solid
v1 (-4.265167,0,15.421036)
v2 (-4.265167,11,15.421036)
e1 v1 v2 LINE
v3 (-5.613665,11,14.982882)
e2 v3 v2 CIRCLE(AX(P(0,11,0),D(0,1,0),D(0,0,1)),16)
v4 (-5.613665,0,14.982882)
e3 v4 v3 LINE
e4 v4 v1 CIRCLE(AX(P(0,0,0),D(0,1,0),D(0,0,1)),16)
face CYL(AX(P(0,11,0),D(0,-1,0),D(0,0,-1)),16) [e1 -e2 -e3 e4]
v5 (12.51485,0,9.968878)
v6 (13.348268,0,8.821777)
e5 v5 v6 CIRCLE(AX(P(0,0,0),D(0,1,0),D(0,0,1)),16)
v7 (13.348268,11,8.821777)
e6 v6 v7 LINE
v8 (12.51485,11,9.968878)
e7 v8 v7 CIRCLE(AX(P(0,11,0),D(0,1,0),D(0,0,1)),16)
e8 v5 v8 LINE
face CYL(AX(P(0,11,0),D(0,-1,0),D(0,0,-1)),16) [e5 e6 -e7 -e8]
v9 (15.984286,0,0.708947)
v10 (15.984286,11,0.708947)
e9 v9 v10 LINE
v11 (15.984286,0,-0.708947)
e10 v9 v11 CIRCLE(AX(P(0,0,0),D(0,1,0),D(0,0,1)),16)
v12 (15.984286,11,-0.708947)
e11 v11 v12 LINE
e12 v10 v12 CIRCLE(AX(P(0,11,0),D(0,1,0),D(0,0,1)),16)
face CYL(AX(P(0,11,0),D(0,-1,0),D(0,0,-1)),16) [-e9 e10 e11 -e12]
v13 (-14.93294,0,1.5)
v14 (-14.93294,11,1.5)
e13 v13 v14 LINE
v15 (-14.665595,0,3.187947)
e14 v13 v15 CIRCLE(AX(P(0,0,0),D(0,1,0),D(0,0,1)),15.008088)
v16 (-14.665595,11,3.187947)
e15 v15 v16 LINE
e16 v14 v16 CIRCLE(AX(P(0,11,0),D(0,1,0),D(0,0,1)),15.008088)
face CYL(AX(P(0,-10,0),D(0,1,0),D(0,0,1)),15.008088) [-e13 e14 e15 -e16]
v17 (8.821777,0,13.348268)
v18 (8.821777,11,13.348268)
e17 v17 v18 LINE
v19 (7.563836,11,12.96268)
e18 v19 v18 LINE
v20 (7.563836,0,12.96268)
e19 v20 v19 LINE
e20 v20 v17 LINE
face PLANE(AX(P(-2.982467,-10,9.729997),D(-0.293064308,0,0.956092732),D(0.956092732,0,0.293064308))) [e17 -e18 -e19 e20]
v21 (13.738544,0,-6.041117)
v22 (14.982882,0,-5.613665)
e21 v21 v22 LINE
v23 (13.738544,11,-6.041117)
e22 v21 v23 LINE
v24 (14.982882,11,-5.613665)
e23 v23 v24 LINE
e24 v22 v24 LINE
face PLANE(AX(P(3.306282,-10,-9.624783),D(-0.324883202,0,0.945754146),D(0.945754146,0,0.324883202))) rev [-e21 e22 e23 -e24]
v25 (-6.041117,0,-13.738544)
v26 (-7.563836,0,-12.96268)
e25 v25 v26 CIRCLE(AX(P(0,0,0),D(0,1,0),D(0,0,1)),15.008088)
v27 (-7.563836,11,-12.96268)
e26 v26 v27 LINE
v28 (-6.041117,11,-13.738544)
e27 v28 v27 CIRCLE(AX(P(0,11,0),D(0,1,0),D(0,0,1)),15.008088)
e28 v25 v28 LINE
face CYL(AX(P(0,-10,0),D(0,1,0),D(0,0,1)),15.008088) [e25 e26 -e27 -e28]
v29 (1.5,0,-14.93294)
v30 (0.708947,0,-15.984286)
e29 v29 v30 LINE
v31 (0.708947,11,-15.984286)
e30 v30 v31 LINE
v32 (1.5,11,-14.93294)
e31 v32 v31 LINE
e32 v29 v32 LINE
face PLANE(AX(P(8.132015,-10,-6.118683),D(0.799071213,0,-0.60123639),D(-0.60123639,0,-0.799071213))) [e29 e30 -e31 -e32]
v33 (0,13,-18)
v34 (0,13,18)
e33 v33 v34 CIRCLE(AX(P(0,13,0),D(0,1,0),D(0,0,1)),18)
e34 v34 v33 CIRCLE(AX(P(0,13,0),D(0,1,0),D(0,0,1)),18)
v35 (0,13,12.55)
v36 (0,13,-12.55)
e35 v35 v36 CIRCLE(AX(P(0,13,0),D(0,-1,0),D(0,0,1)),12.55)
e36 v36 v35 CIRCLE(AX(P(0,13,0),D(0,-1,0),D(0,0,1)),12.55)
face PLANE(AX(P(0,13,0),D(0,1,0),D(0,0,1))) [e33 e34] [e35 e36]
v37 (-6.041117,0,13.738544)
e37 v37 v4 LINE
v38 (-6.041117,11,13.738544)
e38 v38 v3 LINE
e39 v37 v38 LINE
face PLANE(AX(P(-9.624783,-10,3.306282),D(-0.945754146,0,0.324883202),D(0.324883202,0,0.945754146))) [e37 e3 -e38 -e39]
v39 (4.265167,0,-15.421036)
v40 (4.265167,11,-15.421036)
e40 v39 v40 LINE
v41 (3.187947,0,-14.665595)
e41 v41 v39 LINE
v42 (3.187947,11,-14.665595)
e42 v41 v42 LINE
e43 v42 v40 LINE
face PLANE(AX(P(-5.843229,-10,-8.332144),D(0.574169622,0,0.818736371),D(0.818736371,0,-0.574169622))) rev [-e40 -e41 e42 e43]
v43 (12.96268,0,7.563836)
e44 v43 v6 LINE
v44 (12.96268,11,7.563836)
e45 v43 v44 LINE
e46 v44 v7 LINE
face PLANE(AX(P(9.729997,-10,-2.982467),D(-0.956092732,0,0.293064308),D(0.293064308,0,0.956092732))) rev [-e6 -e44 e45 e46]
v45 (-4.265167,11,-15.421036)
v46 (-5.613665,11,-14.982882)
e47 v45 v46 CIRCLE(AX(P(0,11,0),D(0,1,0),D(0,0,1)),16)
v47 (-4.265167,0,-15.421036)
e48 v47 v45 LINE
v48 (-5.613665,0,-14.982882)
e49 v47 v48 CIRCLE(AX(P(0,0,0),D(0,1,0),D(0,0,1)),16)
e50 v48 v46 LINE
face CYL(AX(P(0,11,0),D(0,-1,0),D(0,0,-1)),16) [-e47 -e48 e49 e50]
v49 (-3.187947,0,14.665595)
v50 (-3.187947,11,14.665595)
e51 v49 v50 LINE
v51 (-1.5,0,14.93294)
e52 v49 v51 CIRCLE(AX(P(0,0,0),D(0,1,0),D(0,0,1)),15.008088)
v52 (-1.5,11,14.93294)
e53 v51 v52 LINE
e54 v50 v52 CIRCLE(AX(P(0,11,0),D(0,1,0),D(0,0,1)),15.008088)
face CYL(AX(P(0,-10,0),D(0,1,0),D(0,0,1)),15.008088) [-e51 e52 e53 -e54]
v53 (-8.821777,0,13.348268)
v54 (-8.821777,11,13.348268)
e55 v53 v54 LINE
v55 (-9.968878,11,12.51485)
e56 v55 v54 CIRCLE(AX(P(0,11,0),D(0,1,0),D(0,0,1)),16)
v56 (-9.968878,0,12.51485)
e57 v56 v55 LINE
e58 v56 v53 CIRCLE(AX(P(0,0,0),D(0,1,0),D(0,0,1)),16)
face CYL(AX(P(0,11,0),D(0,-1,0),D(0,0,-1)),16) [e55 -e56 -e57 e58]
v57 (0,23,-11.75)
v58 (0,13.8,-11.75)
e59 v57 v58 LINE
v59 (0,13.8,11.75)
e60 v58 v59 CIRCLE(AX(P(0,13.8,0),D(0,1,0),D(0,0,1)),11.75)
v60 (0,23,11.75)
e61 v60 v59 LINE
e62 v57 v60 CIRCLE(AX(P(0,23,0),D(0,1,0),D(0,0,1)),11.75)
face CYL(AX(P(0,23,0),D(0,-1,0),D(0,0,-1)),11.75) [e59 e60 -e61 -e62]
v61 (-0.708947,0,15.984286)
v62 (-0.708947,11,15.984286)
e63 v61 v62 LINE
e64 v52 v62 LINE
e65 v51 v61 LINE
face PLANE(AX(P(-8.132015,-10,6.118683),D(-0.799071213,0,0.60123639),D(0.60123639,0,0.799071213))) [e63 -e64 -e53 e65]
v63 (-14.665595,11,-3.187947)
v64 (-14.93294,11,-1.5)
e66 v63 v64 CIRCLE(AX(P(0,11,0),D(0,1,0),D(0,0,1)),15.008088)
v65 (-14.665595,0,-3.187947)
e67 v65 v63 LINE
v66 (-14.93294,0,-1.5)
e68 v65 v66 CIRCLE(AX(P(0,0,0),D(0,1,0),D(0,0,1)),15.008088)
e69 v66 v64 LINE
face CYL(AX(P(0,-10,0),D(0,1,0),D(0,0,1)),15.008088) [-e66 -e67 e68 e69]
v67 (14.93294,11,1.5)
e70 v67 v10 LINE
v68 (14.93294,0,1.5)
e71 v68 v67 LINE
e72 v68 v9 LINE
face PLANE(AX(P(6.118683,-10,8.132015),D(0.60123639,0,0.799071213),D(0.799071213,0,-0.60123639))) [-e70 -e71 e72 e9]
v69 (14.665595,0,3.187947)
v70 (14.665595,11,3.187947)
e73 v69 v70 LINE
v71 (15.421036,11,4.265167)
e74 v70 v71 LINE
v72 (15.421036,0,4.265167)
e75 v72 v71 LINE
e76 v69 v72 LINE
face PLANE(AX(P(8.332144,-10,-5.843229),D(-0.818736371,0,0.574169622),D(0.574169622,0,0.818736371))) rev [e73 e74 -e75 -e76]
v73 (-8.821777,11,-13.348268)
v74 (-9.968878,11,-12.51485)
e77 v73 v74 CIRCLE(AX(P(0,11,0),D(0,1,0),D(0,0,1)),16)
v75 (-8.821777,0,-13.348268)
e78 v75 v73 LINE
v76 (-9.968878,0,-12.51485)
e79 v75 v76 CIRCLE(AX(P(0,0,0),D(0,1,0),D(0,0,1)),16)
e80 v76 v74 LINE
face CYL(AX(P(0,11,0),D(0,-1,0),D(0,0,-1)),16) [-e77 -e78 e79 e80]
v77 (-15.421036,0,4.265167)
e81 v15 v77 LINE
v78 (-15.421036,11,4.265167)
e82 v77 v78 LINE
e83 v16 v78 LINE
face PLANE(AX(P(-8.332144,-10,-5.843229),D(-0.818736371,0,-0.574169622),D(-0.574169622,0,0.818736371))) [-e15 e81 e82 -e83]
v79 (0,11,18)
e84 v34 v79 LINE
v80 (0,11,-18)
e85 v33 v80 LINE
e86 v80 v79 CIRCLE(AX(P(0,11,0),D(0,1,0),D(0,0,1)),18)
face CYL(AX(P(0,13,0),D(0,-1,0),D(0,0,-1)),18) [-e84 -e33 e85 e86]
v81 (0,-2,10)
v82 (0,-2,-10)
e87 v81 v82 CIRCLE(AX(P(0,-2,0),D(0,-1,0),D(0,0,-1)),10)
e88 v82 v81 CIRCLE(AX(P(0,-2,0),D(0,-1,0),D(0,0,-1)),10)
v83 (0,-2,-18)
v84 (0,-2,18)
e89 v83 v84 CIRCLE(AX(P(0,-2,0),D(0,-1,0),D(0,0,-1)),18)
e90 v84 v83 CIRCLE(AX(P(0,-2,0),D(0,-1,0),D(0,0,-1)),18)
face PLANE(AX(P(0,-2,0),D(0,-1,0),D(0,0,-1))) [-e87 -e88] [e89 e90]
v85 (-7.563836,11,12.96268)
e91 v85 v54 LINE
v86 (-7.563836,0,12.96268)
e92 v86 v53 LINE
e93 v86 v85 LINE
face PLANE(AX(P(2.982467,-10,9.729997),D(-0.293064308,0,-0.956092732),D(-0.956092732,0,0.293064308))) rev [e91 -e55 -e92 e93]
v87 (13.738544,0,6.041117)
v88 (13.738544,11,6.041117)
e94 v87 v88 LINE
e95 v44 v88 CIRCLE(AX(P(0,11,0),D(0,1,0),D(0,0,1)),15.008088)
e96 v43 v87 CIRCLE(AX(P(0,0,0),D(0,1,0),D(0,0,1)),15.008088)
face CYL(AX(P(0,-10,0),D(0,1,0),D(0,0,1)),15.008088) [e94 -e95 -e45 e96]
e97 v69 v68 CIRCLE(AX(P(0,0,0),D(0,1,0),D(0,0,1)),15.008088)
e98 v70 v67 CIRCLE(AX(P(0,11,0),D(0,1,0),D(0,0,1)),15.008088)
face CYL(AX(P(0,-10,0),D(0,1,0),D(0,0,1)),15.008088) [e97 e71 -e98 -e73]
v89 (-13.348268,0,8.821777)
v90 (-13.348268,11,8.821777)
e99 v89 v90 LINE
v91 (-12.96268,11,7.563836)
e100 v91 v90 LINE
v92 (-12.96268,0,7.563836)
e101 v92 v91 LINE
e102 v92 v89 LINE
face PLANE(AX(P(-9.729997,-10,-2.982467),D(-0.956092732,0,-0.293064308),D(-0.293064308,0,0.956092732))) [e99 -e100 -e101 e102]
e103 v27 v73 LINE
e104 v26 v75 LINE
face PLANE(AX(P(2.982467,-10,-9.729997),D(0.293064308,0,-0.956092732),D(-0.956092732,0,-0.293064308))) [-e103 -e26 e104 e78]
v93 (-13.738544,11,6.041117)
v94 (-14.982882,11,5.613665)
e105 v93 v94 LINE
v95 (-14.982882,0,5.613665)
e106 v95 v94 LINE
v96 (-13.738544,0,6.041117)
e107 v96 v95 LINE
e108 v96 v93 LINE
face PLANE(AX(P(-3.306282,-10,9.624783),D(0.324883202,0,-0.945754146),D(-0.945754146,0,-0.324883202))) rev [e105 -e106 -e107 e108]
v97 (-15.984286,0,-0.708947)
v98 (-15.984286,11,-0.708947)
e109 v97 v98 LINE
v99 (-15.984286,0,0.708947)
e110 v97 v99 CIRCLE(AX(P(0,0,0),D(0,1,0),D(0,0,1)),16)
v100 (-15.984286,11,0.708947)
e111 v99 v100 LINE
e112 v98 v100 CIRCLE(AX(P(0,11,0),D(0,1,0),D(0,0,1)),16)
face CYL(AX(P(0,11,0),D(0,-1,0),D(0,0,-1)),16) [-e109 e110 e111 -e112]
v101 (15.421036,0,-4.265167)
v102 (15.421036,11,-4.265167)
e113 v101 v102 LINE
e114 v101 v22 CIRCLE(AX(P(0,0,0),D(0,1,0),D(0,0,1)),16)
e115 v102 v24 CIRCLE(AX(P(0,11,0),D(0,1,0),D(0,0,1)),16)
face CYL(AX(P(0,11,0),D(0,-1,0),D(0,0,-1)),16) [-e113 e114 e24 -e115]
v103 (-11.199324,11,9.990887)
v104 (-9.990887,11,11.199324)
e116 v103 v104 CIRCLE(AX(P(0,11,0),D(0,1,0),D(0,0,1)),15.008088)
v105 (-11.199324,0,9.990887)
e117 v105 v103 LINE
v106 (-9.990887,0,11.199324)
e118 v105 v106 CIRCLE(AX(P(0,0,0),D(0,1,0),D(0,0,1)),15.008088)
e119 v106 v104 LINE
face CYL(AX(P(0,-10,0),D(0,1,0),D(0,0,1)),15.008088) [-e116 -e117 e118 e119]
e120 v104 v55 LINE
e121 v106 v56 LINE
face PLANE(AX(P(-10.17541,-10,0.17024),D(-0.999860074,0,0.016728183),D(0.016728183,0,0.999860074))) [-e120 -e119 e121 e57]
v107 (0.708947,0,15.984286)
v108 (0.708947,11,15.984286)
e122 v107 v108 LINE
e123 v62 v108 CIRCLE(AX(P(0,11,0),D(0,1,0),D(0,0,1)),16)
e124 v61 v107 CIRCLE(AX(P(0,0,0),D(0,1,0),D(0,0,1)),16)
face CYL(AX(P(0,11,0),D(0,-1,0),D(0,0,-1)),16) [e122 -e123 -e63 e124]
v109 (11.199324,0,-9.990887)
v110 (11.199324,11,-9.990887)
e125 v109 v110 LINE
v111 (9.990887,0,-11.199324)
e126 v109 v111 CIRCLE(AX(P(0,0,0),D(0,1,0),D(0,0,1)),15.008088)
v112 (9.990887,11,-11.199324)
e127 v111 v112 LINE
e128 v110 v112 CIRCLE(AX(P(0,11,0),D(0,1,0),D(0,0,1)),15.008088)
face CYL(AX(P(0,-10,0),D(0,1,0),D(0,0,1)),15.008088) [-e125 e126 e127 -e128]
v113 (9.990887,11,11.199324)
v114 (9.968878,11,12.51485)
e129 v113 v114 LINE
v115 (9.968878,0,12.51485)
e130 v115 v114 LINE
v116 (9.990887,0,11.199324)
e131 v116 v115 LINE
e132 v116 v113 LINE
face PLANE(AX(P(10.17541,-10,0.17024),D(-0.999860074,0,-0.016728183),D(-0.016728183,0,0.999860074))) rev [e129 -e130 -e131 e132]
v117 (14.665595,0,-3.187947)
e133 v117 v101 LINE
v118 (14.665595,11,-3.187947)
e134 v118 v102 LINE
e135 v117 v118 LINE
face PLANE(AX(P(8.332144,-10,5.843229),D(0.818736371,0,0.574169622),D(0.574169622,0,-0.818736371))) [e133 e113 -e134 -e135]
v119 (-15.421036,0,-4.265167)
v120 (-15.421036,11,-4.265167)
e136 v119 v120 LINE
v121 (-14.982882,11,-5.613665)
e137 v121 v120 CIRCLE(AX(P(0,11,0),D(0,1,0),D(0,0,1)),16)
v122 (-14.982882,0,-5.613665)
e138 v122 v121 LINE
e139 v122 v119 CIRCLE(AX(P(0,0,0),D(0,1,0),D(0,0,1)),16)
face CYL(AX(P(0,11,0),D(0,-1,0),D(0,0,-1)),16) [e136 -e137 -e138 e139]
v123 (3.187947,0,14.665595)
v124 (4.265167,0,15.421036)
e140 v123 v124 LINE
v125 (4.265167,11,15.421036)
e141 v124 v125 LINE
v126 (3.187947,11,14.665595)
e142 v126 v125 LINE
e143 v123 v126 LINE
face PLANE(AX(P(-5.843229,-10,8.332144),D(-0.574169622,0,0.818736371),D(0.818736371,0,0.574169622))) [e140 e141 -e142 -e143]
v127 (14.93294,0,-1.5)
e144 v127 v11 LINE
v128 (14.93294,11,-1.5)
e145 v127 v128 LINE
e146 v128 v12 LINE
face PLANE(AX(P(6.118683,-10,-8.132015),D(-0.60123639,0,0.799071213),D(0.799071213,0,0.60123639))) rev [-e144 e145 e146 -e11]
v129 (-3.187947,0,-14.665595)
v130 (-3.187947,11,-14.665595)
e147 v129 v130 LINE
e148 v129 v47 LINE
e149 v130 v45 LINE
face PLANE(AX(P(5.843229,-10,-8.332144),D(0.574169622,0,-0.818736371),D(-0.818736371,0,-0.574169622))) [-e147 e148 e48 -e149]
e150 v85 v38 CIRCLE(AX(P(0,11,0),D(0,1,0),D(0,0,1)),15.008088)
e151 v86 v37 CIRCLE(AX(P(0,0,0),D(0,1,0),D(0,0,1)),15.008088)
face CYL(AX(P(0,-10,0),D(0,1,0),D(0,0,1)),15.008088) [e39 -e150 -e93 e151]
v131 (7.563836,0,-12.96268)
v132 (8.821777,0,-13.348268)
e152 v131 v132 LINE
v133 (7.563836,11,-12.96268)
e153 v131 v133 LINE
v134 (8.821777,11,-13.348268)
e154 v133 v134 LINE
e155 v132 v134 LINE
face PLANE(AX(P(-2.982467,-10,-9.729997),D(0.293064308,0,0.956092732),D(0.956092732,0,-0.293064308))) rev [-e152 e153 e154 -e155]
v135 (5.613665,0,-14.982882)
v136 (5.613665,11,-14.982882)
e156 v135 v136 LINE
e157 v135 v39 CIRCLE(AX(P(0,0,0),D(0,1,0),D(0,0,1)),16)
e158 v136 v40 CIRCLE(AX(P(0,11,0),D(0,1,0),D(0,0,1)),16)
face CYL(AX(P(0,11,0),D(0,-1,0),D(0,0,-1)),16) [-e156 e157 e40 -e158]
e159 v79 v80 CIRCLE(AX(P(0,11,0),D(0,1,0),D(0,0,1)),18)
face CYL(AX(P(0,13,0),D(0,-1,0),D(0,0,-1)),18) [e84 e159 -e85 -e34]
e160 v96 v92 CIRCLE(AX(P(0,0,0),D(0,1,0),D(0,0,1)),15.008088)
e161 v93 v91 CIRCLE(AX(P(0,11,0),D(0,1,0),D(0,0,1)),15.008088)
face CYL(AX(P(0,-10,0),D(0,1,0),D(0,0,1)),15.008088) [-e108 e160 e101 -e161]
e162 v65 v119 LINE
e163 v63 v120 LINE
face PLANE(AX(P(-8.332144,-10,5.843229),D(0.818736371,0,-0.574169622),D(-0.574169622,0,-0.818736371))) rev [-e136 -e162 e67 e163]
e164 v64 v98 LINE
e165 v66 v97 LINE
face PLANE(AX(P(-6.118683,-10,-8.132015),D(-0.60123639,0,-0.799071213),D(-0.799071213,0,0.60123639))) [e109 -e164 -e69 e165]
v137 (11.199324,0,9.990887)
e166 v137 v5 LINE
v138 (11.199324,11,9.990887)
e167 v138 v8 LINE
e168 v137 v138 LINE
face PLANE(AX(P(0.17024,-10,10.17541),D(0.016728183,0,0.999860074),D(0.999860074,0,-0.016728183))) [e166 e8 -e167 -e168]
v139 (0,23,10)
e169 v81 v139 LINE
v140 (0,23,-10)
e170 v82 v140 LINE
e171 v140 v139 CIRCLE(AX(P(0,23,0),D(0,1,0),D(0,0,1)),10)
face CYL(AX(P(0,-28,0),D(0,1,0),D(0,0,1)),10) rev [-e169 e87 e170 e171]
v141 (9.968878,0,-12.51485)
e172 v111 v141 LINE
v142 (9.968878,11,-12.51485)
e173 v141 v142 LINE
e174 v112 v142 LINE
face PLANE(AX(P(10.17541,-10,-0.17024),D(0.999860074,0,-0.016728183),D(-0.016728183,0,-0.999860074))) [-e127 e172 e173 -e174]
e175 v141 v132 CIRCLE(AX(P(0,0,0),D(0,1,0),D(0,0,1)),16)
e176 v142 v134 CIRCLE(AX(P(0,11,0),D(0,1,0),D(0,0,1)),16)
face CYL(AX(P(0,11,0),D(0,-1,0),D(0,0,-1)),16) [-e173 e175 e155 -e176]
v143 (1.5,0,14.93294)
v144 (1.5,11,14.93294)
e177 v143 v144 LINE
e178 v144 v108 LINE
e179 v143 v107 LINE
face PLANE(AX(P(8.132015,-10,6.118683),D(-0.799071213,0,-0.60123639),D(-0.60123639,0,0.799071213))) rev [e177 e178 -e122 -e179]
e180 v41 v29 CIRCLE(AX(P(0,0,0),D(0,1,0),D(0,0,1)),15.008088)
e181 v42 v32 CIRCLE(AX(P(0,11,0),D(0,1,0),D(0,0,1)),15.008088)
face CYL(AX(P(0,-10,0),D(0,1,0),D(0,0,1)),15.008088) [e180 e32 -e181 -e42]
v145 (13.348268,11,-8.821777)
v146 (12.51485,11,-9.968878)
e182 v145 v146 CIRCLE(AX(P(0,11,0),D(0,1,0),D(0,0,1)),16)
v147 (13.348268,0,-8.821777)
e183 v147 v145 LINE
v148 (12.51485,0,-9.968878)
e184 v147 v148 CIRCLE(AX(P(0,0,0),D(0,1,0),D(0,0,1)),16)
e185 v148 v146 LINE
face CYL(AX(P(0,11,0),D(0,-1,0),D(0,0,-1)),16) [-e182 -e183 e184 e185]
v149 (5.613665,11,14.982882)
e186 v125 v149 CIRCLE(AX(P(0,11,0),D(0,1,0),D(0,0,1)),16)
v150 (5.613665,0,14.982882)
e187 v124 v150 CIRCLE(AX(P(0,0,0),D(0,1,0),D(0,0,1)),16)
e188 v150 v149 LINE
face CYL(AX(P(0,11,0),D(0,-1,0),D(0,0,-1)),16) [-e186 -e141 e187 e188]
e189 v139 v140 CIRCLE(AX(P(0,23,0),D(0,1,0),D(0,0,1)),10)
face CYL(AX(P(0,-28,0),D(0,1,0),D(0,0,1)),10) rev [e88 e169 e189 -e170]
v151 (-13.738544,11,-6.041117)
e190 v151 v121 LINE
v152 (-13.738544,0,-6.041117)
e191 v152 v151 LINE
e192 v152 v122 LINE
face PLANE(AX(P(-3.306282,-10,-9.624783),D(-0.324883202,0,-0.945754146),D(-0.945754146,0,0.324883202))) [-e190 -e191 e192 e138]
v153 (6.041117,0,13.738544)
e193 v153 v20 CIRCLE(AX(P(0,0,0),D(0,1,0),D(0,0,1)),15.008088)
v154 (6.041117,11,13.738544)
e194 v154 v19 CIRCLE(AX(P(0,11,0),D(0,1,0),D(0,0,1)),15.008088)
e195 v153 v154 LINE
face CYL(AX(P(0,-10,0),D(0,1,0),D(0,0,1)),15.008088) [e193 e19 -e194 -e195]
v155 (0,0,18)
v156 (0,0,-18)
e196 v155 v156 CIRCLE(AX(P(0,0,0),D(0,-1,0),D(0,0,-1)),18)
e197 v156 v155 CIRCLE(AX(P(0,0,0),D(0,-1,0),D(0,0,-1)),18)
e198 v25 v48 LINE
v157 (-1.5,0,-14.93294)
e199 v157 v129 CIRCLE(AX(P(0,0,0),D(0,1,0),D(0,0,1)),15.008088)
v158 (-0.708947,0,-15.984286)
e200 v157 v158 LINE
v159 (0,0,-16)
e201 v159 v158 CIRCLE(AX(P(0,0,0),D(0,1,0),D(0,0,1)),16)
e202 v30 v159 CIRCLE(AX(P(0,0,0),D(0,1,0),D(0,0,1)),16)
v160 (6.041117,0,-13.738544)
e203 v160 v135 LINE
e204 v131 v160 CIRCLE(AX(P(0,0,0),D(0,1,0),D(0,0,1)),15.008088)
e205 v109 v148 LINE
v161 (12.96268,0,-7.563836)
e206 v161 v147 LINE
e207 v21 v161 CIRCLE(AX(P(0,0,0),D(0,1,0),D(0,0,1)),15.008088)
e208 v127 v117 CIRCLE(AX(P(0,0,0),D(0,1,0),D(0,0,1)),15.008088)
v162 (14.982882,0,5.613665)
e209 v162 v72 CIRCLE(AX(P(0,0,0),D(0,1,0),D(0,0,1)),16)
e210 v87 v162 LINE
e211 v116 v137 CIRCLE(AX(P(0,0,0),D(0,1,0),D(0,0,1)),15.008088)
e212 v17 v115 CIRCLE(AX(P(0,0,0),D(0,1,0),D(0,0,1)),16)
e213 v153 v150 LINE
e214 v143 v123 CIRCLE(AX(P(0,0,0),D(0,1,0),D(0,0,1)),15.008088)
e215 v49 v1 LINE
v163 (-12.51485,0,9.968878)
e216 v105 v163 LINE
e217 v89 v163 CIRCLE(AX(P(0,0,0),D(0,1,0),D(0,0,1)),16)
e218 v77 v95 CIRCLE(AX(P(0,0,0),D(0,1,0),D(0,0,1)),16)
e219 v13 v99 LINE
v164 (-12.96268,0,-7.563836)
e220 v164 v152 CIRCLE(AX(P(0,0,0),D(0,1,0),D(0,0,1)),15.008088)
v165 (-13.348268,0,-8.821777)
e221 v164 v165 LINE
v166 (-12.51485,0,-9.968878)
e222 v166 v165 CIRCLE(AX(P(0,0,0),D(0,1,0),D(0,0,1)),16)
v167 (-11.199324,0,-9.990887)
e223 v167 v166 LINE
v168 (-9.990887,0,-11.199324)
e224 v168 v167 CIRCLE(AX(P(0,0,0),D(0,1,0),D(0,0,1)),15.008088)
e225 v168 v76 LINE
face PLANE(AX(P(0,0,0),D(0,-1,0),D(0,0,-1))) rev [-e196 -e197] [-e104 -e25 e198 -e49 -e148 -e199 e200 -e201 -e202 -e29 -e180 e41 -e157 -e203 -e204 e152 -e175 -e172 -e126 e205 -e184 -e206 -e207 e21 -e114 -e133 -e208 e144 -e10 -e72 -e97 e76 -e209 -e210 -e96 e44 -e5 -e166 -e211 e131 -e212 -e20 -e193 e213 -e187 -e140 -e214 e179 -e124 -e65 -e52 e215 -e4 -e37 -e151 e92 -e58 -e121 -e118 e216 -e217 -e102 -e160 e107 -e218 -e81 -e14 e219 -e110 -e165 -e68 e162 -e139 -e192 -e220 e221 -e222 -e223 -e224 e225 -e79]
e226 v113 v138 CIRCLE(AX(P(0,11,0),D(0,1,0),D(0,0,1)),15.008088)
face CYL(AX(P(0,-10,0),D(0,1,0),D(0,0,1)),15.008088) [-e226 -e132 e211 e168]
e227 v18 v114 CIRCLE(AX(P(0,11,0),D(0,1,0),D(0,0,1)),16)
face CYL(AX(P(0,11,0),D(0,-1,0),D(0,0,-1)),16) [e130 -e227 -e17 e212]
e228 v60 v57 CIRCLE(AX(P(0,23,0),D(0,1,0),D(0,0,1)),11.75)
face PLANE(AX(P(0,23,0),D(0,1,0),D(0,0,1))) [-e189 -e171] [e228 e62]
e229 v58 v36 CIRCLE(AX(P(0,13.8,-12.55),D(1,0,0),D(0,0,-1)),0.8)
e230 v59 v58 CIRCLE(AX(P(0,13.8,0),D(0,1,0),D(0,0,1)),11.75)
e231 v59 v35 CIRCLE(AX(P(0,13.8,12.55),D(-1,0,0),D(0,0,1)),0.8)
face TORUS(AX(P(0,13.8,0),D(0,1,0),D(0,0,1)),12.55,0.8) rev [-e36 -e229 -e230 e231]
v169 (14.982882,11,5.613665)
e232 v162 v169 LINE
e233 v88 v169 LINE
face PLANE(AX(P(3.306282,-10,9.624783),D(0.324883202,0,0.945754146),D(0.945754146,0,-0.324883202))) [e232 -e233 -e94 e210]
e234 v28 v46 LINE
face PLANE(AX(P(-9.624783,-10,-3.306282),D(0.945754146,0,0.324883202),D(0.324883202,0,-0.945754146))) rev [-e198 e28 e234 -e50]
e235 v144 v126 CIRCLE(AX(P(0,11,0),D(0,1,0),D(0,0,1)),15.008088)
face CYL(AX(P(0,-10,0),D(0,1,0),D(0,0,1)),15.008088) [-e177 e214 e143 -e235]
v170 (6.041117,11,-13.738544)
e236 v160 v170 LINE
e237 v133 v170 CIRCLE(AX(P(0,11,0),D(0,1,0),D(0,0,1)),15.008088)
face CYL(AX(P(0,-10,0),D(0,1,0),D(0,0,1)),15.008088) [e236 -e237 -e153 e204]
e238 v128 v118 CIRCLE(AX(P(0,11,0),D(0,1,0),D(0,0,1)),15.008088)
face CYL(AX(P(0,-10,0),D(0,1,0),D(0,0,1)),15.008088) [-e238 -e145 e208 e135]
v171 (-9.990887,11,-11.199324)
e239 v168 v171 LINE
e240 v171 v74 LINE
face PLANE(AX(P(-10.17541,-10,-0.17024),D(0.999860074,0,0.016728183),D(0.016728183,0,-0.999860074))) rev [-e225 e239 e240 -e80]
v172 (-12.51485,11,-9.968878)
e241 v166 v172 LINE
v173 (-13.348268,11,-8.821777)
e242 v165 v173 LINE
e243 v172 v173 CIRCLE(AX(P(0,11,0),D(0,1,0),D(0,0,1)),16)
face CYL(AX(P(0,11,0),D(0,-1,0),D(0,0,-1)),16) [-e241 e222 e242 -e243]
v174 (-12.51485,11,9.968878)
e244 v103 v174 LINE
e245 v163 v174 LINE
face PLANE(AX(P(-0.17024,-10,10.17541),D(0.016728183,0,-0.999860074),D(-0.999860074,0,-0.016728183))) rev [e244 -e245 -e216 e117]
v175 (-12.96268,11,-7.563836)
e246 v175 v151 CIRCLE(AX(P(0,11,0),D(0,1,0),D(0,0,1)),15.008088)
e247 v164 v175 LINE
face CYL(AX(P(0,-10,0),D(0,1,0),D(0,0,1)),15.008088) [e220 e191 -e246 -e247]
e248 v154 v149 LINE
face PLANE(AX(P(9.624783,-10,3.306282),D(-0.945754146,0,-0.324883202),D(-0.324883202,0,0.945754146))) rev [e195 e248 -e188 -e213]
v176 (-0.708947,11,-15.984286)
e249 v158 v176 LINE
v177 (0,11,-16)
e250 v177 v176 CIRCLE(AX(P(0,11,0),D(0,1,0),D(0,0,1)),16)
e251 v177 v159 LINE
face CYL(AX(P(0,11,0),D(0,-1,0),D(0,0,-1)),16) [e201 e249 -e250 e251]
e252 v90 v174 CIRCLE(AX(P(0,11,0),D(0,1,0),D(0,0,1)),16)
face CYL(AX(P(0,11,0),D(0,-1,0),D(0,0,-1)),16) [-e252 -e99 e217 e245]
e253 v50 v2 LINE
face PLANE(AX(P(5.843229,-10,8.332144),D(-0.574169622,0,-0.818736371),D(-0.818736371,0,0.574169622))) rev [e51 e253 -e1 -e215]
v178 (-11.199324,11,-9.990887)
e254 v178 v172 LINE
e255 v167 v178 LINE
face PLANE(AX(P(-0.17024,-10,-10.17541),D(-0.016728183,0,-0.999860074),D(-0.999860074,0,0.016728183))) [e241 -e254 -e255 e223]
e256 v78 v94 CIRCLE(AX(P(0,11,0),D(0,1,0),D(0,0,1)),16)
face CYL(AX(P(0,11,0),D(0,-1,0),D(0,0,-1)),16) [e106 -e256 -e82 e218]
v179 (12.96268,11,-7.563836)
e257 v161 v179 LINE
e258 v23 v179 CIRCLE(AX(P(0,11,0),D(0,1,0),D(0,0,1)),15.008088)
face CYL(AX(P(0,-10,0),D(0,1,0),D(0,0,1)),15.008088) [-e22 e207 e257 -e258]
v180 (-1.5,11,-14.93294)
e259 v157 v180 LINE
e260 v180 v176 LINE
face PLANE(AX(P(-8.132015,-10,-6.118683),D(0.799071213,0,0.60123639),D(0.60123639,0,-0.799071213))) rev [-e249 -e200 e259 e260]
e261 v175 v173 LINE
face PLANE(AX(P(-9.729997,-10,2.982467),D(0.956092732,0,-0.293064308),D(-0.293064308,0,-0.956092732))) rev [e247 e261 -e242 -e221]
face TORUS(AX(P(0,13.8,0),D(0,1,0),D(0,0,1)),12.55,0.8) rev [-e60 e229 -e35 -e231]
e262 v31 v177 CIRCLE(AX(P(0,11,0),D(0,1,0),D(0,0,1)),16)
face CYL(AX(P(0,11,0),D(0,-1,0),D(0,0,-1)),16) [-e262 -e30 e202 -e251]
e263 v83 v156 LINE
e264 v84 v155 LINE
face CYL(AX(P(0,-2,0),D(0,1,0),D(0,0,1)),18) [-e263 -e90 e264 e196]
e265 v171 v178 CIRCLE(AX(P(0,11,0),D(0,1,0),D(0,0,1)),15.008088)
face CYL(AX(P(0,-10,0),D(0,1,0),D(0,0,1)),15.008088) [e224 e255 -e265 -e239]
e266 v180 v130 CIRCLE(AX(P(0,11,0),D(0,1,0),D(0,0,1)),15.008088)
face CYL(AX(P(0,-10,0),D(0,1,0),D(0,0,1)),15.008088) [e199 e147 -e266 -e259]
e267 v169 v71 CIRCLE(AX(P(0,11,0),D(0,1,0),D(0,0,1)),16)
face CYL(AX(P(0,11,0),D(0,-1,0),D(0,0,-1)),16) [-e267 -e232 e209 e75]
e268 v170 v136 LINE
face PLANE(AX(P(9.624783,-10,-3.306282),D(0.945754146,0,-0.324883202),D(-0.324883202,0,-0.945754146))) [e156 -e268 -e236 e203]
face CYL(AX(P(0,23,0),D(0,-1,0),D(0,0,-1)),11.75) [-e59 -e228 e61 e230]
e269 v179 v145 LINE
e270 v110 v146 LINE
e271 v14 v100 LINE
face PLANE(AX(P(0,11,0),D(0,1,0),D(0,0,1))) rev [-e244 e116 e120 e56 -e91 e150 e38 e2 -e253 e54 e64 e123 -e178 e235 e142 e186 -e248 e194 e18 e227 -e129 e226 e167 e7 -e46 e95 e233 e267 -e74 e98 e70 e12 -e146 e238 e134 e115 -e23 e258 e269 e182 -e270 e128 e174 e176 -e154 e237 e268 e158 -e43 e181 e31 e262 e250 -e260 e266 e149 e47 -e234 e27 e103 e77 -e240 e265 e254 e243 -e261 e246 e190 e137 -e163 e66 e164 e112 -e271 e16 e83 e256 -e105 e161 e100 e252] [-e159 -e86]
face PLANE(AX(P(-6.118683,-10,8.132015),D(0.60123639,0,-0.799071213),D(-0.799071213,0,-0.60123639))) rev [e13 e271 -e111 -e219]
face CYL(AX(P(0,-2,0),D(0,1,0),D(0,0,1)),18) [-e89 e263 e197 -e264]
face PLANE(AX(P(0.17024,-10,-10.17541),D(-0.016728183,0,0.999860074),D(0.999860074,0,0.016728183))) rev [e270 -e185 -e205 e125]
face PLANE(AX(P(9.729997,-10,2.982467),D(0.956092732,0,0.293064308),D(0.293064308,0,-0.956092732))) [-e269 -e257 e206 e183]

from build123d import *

# Parameters (mm, degrees)
SKETCH1_R           = 16
BOSS_EXTRUDE1_DEPTH = 11
CUT_EXTRUDE2_START  = -21
CUT_EXTRUDE2_DEPTH  = 21
SKETCH3_R           = 18
BOSS_EXTRUDE2_DEPTH = 2
BOSS_EXTRUDE3_START = 2
SKETCH4_R           = 18
BOSS_EXTRUDE3_DEPTH = 2
SKETCH5_R           = 11.75
BOSS_EXTRUDE4_DEPTH = 10
FILLET1_R           = 0.8
SKETCH6_R           = 10
CUT_EXTRUDE3_DEPTH  = 51


with BuildPart() as part:
    # Sketch1 → Boss-Extrude1 (new body)
    with BuildSketch(Plane(origin=(0, 0, 0), x_dir=(1, 0, 0), z_dir=(0, 1, 0))):
        with Locations(Location((0, 0, 0), (0, 0, 270))):
            Circle(SKETCH1_R)
    extrude(amount=BOSS_EXTRUDE1_DEPTH)

    # Sketch2 → Cut-Extrude2 (cut)
    with BuildSketch(Plane(origin=(0, 11, 0), x_dir=(1, 0, 0), z_dir=(0, 1, 0)).offset(CUT_EXTRUDE2_START)):
        with BuildLine():
            ThreePointArc((4.265167024, 15.421035966), (2.502951441, 15.80301345), (0.708947293, 15.984285838))
            Line((0.708947293, 15.984285838), (1.5, 14.932939883))
            ThreePointArc((1.5, 14.932939883), (2.347782156, 14.823313142), (3.187947426, 14.665595275))
            Line((3.187947426, 14.665595275), (4.265167024, 15.421035966))
        make_face()
        with BuildLine():
            ThreePointArc((8.821777076, 13.348267649), (7.263847996, 14.256104387), (5.613664909, 14.982882443))
            Line((5.613664909, 14.982882443), (6.041116974, 13.738544292))
            ThreePointArc((6.041116974, 13.738544292), (6.813529192, 13.372303972), (7.563836345, 12.96268002))
            Line((7.563836345, 12.96268002), (8.821777076, 13.348267649))
        make_face()
        with BuildLine():
            ThreePointArc((12.514850122, 9.968877892), (11.313708499, 11.313708499), (9.968877892, 12.514850122))
            Line((9.968877892, 12.514850122), (9.990887328, 11.199324263))
            ThreePointArc((9.990887328, 11.199324263), (10.612320518, 10.612320518), (11.199324263, 9.990887328))
            Line((11.199324263, 9.990887328), (12.514850122, 9.968877892))
        make_face()
        with BuildLine():
            ThreePointArc((14.982882443, 5.613664909), (14.256104387, 7.263847996), (13.348267649, 8.821777076))
            Line((13.348267649, 8.821777076), (12.96268002, 7.563836345))
            ThreePointArc((12.96268002, 7.563836345), (13.372303972, 6.813529192), (13.738544292, 6.041116974))
            Line((13.738544292, 6.041116974), (14.982882443, 5.613664909))
        make_face()
        with BuildLine():
            ThreePointArc((15.984285838, 0.708947293), (15.80301345, 2.502951441), (15.421035966, 4.265167024))
            Line((15.421035966, 4.265167024), (14.665595275, 3.187947426))
            ThreePointArc((14.665595275, 3.187947426), (14.823313142, 2.347782156), (14.932939883, 1.5))
            Line((14.932939883, 1.5), (15.984285838, 0.708947293))
        make_face()
        with BuildLine():
            ThreePointArc((15.421035966, -4.265167024), (15.80301345, -2.502951441), (15.984285838, -0.708947293))
            Line((15.984285838, -0.708947293), (14.932939883, -1.5))
            ThreePointArc((14.932939883, -1.5), (14.823313142, -2.347782156), (14.665595275, -3.187947426))
            Line((14.665595275, -3.187947426), (15.421035966, -4.265167024))
        make_face()
        with BuildLine():
            ThreePointArc((13.348267649, -8.821777076), (14.256104387, -7.263847996), (14.982882443, -5.613664909))
            Line((14.982882443, -5.613664909), (13.738544292, -6.041116974))
            ThreePointArc((13.738544292, -6.041116974), (13.372303972, -6.813529192), (12.96268002, -7.563836345))
            Line((12.96268002, -7.563836345), (13.348267649, -8.821777076))
        make_face()
        with BuildLine():
            ThreePointArc((9.968877892, -12.514850122), (11.313708499, -11.313708499), (12.514850122, -9.968877892))
            Line((12.514850122, -9.968877892), (11.199324263, -9.990887328))
            ThreePointArc((11.199324263, -9.990887328), (10.612320518, -10.612320518), (9.990887328, -11.199324263))
            Line((9.990887328, -11.199324263), (9.968877892, -12.514850122))
        make_face()
        with BuildLine():
            ThreePointArc((5.613664909, -14.982882443), (7.263847996, -14.256104387), (8.821777076, -13.348267649))
            Line((8.821777076, -13.348267649), (7.563836345, -12.96268002))
            ThreePointArc((7.563836345, -12.96268002), (6.813529192, -13.372303972), (6.041116974, -13.738544292))
            Line((6.041116974, -13.738544292), (5.613664909, -14.982882443))
        make_face()
        with BuildLine():
            Line((1.5, -14.932939883), (0.708947293, -15.984285838))
            ThreePointArc((0.708947293, -15.984285838), (2.502951441, -15.80301345), (4.265167024, -15.421035966))
            Line((4.265167024, -15.421035966), (3.187947426, -14.665595275))
            ThreePointArc((3.187947426, -14.665595275), (2.347782156, -14.823313142), (1.5, -14.932939883))
        make_face()
        with BuildLine():
            Line((-3.187947426, -14.665595275), (-4.265167024, -15.421035966))
            ThreePointArc((-4.265167024, -15.421035966), (-2.502951441, -15.80301345), (-0.708947293, -15.984285838))
            Line((-0.708947293, -15.984285838), (-1.5, -14.932939883))
            ThreePointArc((-1.5, -14.932939883), (-2.347782156, -14.823313142), (-3.187947426, -14.665595275))
        make_face()
        with BuildLine():
            Line((-7.563836345, -12.96268002), (-8.821777076, -13.348267649))
            ThreePointArc((-8.821777076, -13.348267649), (-7.263847996, -14.256104387), (-5.613664909, -14.982882443))
            Line((-5.613664909, -14.982882443), (-6.041116974, -13.738544292))
            ThreePointArc((-6.041116974, -13.738544292), (-6.813529192, -13.372303972), (-7.563836345, -12.96268002))
        make_face()
        with BuildLine():
            Line((-11.199324263, -9.990887328), (-12.514850122, -9.968877892))
            ThreePointArc((-12.514850122, -9.968877892), (-11.313708499, -11.313708499), (-9.968877892, -12.514850122))
            Line((-9.968877892, -12.514850122), (-9.990887328, -11.199324263))
            ThreePointArc((-9.990887328, -11.199324263), (-10.612320518, -10.612320518), (-11.199324263, -9.990887328))
        make_face()
        with BuildLine():
            Line((-13.738544292, -6.041116974), (-14.982882443, -5.613664909))
            ThreePointArc((-14.982882443, -5.613664909), (-14.256104387, -7.263847996), (-13.348267649, -8.821777076))
            Line((-13.348267649, -8.821777076), (-12.96268002, -7.563836345))
            ThreePointArc((-12.96268002, -7.563836345), (-13.372303972, -6.813529192), (-13.738544292, -6.041116974))
        make_face()
        with BuildLine():
            Line((-14.932939883, -1.5), (-15.984285838, -0.708947293))
            ThreePointArc((-15.984285838, -0.708947293), (-15.80301345, -2.502951441), (-15.421035966, -4.265167024))
            Line((-15.421035966, -4.265167024), (-14.665595275, -3.187947426))
            ThreePointArc((-14.665595275, -3.187947426), (-14.823313142, -2.347782156), (-14.932939883, -1.5))
        make_face()
        with BuildLine():
            Line((-14.665595275, 3.187947426), (-15.421035966, 4.265167024))
            ThreePointArc((-15.421035966, 4.265167024), (-15.80301345, 2.502951441), (-15.984285838, 0.708947293))
            Line((-15.984285838, 0.708947293), (-14.932939883, 1.5))
            ThreePointArc((-14.932939883, 1.5), (-14.823313142, 2.347782156), (-14.665595275, 3.187947426))
        make_face()
        with BuildLine():
            Line((-12.96268002, 7.563836345), (-13.348267649, 8.821777076))
            ThreePointArc((-13.348267649, 8.821777076), (-14.256104387, 7.263847996), (-14.982882443, 5.613664909))
            Line((-14.982882443, 5.613664909), (-13.738544292, 6.041116974))
            ThreePointArc((-13.738544292, 6.041116974), (-13.372303972, 6.813529192), (-12.96268002, 7.563836345))
        make_face()
        with BuildLine():
            Line((-9.990887328, 11.199324263), (-9.968877892, 12.514850122))
            ThreePointArc((-9.968877892, 12.514850122), (-11.313708499, 11.313708499), (-12.514850122, 9.968877892))
            Line((-12.514850122, 9.968877892), (-11.199324263, 9.990887328))
            ThreePointArc((-11.199324263, 9.990887328), (-10.612320518, 10.612320518), (-9.990887328, 11.199324263))
        make_face()
        with BuildLine():
            Line((-6.041116974, 13.738544292), (-5.613664909, 14.982882443))
            ThreePointArc((-5.613664909, 14.982882443), (-7.263847996, 14.256104387), (-8.821777076, 13.348267649))
            Line((-8.821777076, 13.348267649), (-7.563836345, 12.96268002))
            ThreePointArc((-7.563836345, 12.96268002), (-6.813529192, 13.372303972), (-6.041116974, 13.738544292))
        make_face()
        with BuildLine():
            ThreePointArc((-3.187947426, 14.665595275), (-2.347782156, 14.823313142), (-1.5, 14.932939883))
            Line((-1.5, 14.932939883), (-0.708947293, 15.984285838))
            ThreePointArc((-0.708947293, 15.984285838), (-2.502951441, 15.80301345), (-4.265167024, 15.421035966))
            Line((-4.265167024, 15.421035966), (-3.187947426, 14.665595275))
        make_face()
    extrude(amount=CUT_EXTRUDE2_DEPTH, mode=Mode.SUBTRACT)

    # Sketch3 → Boss-Extrude2 (add)
    with BuildSketch(Plane(origin=(0, 11, 0), x_dir=(1, 0, 0), z_dir=(0, 1, 0))):
        with Locations(Location((0, 0, 0), (0, 0, 270))):
            Circle(SKETCH3_R)
    extrude(amount=BOSS_EXTRUDE2_DEPTH)

    # Sketch4 → Boss-Extrude3 (add)
    with BuildSketch(Plane.XZ.offset(BOSS_EXTRUDE3_START)):
        with Locations(Location((0, 0, 0), (0, 0, 90))):
            Circle(SKETCH4_R)
    extrude(amount=-BOSS_EXTRUDE3_DEPTH)

    # Sketch5 → Boss-Extrude4 (add)
    with BuildSketch(Plane(origin=(0, 13, 0), x_dir=(1, 0, 0), z_dir=(0, 1, 0))):
        with Locations(Location((0, 0, 0), (0, 0, 270))):
            Circle(SKETCH5_R)
    extrude(amount=BOSS_EXTRUDE4_DEPTH)

    # Fillet1
    fillet1_edges = [part.edges().sort_by_distance(p)[0] for p in [
        (0, 13, -11.75),
    ]]
    fillet(fillet1_edges, radius=FILLET1_R)

    # Sketch6 → Cut-Extrude3 (cut)
    with BuildSketch(Plane(origin=(0, 23, 0), x_dir=(1, 0, 0), z_dir=(0, 1, 0))):
        with Locations(Location((0, 0, 0), (0, 0, 270))):
            Circle(SKETCH6_R)
    extrude(amount=-CUT_EXTRUDE3_DEPTH, mode=Mode.SUBTRACT)


solid = part.part
